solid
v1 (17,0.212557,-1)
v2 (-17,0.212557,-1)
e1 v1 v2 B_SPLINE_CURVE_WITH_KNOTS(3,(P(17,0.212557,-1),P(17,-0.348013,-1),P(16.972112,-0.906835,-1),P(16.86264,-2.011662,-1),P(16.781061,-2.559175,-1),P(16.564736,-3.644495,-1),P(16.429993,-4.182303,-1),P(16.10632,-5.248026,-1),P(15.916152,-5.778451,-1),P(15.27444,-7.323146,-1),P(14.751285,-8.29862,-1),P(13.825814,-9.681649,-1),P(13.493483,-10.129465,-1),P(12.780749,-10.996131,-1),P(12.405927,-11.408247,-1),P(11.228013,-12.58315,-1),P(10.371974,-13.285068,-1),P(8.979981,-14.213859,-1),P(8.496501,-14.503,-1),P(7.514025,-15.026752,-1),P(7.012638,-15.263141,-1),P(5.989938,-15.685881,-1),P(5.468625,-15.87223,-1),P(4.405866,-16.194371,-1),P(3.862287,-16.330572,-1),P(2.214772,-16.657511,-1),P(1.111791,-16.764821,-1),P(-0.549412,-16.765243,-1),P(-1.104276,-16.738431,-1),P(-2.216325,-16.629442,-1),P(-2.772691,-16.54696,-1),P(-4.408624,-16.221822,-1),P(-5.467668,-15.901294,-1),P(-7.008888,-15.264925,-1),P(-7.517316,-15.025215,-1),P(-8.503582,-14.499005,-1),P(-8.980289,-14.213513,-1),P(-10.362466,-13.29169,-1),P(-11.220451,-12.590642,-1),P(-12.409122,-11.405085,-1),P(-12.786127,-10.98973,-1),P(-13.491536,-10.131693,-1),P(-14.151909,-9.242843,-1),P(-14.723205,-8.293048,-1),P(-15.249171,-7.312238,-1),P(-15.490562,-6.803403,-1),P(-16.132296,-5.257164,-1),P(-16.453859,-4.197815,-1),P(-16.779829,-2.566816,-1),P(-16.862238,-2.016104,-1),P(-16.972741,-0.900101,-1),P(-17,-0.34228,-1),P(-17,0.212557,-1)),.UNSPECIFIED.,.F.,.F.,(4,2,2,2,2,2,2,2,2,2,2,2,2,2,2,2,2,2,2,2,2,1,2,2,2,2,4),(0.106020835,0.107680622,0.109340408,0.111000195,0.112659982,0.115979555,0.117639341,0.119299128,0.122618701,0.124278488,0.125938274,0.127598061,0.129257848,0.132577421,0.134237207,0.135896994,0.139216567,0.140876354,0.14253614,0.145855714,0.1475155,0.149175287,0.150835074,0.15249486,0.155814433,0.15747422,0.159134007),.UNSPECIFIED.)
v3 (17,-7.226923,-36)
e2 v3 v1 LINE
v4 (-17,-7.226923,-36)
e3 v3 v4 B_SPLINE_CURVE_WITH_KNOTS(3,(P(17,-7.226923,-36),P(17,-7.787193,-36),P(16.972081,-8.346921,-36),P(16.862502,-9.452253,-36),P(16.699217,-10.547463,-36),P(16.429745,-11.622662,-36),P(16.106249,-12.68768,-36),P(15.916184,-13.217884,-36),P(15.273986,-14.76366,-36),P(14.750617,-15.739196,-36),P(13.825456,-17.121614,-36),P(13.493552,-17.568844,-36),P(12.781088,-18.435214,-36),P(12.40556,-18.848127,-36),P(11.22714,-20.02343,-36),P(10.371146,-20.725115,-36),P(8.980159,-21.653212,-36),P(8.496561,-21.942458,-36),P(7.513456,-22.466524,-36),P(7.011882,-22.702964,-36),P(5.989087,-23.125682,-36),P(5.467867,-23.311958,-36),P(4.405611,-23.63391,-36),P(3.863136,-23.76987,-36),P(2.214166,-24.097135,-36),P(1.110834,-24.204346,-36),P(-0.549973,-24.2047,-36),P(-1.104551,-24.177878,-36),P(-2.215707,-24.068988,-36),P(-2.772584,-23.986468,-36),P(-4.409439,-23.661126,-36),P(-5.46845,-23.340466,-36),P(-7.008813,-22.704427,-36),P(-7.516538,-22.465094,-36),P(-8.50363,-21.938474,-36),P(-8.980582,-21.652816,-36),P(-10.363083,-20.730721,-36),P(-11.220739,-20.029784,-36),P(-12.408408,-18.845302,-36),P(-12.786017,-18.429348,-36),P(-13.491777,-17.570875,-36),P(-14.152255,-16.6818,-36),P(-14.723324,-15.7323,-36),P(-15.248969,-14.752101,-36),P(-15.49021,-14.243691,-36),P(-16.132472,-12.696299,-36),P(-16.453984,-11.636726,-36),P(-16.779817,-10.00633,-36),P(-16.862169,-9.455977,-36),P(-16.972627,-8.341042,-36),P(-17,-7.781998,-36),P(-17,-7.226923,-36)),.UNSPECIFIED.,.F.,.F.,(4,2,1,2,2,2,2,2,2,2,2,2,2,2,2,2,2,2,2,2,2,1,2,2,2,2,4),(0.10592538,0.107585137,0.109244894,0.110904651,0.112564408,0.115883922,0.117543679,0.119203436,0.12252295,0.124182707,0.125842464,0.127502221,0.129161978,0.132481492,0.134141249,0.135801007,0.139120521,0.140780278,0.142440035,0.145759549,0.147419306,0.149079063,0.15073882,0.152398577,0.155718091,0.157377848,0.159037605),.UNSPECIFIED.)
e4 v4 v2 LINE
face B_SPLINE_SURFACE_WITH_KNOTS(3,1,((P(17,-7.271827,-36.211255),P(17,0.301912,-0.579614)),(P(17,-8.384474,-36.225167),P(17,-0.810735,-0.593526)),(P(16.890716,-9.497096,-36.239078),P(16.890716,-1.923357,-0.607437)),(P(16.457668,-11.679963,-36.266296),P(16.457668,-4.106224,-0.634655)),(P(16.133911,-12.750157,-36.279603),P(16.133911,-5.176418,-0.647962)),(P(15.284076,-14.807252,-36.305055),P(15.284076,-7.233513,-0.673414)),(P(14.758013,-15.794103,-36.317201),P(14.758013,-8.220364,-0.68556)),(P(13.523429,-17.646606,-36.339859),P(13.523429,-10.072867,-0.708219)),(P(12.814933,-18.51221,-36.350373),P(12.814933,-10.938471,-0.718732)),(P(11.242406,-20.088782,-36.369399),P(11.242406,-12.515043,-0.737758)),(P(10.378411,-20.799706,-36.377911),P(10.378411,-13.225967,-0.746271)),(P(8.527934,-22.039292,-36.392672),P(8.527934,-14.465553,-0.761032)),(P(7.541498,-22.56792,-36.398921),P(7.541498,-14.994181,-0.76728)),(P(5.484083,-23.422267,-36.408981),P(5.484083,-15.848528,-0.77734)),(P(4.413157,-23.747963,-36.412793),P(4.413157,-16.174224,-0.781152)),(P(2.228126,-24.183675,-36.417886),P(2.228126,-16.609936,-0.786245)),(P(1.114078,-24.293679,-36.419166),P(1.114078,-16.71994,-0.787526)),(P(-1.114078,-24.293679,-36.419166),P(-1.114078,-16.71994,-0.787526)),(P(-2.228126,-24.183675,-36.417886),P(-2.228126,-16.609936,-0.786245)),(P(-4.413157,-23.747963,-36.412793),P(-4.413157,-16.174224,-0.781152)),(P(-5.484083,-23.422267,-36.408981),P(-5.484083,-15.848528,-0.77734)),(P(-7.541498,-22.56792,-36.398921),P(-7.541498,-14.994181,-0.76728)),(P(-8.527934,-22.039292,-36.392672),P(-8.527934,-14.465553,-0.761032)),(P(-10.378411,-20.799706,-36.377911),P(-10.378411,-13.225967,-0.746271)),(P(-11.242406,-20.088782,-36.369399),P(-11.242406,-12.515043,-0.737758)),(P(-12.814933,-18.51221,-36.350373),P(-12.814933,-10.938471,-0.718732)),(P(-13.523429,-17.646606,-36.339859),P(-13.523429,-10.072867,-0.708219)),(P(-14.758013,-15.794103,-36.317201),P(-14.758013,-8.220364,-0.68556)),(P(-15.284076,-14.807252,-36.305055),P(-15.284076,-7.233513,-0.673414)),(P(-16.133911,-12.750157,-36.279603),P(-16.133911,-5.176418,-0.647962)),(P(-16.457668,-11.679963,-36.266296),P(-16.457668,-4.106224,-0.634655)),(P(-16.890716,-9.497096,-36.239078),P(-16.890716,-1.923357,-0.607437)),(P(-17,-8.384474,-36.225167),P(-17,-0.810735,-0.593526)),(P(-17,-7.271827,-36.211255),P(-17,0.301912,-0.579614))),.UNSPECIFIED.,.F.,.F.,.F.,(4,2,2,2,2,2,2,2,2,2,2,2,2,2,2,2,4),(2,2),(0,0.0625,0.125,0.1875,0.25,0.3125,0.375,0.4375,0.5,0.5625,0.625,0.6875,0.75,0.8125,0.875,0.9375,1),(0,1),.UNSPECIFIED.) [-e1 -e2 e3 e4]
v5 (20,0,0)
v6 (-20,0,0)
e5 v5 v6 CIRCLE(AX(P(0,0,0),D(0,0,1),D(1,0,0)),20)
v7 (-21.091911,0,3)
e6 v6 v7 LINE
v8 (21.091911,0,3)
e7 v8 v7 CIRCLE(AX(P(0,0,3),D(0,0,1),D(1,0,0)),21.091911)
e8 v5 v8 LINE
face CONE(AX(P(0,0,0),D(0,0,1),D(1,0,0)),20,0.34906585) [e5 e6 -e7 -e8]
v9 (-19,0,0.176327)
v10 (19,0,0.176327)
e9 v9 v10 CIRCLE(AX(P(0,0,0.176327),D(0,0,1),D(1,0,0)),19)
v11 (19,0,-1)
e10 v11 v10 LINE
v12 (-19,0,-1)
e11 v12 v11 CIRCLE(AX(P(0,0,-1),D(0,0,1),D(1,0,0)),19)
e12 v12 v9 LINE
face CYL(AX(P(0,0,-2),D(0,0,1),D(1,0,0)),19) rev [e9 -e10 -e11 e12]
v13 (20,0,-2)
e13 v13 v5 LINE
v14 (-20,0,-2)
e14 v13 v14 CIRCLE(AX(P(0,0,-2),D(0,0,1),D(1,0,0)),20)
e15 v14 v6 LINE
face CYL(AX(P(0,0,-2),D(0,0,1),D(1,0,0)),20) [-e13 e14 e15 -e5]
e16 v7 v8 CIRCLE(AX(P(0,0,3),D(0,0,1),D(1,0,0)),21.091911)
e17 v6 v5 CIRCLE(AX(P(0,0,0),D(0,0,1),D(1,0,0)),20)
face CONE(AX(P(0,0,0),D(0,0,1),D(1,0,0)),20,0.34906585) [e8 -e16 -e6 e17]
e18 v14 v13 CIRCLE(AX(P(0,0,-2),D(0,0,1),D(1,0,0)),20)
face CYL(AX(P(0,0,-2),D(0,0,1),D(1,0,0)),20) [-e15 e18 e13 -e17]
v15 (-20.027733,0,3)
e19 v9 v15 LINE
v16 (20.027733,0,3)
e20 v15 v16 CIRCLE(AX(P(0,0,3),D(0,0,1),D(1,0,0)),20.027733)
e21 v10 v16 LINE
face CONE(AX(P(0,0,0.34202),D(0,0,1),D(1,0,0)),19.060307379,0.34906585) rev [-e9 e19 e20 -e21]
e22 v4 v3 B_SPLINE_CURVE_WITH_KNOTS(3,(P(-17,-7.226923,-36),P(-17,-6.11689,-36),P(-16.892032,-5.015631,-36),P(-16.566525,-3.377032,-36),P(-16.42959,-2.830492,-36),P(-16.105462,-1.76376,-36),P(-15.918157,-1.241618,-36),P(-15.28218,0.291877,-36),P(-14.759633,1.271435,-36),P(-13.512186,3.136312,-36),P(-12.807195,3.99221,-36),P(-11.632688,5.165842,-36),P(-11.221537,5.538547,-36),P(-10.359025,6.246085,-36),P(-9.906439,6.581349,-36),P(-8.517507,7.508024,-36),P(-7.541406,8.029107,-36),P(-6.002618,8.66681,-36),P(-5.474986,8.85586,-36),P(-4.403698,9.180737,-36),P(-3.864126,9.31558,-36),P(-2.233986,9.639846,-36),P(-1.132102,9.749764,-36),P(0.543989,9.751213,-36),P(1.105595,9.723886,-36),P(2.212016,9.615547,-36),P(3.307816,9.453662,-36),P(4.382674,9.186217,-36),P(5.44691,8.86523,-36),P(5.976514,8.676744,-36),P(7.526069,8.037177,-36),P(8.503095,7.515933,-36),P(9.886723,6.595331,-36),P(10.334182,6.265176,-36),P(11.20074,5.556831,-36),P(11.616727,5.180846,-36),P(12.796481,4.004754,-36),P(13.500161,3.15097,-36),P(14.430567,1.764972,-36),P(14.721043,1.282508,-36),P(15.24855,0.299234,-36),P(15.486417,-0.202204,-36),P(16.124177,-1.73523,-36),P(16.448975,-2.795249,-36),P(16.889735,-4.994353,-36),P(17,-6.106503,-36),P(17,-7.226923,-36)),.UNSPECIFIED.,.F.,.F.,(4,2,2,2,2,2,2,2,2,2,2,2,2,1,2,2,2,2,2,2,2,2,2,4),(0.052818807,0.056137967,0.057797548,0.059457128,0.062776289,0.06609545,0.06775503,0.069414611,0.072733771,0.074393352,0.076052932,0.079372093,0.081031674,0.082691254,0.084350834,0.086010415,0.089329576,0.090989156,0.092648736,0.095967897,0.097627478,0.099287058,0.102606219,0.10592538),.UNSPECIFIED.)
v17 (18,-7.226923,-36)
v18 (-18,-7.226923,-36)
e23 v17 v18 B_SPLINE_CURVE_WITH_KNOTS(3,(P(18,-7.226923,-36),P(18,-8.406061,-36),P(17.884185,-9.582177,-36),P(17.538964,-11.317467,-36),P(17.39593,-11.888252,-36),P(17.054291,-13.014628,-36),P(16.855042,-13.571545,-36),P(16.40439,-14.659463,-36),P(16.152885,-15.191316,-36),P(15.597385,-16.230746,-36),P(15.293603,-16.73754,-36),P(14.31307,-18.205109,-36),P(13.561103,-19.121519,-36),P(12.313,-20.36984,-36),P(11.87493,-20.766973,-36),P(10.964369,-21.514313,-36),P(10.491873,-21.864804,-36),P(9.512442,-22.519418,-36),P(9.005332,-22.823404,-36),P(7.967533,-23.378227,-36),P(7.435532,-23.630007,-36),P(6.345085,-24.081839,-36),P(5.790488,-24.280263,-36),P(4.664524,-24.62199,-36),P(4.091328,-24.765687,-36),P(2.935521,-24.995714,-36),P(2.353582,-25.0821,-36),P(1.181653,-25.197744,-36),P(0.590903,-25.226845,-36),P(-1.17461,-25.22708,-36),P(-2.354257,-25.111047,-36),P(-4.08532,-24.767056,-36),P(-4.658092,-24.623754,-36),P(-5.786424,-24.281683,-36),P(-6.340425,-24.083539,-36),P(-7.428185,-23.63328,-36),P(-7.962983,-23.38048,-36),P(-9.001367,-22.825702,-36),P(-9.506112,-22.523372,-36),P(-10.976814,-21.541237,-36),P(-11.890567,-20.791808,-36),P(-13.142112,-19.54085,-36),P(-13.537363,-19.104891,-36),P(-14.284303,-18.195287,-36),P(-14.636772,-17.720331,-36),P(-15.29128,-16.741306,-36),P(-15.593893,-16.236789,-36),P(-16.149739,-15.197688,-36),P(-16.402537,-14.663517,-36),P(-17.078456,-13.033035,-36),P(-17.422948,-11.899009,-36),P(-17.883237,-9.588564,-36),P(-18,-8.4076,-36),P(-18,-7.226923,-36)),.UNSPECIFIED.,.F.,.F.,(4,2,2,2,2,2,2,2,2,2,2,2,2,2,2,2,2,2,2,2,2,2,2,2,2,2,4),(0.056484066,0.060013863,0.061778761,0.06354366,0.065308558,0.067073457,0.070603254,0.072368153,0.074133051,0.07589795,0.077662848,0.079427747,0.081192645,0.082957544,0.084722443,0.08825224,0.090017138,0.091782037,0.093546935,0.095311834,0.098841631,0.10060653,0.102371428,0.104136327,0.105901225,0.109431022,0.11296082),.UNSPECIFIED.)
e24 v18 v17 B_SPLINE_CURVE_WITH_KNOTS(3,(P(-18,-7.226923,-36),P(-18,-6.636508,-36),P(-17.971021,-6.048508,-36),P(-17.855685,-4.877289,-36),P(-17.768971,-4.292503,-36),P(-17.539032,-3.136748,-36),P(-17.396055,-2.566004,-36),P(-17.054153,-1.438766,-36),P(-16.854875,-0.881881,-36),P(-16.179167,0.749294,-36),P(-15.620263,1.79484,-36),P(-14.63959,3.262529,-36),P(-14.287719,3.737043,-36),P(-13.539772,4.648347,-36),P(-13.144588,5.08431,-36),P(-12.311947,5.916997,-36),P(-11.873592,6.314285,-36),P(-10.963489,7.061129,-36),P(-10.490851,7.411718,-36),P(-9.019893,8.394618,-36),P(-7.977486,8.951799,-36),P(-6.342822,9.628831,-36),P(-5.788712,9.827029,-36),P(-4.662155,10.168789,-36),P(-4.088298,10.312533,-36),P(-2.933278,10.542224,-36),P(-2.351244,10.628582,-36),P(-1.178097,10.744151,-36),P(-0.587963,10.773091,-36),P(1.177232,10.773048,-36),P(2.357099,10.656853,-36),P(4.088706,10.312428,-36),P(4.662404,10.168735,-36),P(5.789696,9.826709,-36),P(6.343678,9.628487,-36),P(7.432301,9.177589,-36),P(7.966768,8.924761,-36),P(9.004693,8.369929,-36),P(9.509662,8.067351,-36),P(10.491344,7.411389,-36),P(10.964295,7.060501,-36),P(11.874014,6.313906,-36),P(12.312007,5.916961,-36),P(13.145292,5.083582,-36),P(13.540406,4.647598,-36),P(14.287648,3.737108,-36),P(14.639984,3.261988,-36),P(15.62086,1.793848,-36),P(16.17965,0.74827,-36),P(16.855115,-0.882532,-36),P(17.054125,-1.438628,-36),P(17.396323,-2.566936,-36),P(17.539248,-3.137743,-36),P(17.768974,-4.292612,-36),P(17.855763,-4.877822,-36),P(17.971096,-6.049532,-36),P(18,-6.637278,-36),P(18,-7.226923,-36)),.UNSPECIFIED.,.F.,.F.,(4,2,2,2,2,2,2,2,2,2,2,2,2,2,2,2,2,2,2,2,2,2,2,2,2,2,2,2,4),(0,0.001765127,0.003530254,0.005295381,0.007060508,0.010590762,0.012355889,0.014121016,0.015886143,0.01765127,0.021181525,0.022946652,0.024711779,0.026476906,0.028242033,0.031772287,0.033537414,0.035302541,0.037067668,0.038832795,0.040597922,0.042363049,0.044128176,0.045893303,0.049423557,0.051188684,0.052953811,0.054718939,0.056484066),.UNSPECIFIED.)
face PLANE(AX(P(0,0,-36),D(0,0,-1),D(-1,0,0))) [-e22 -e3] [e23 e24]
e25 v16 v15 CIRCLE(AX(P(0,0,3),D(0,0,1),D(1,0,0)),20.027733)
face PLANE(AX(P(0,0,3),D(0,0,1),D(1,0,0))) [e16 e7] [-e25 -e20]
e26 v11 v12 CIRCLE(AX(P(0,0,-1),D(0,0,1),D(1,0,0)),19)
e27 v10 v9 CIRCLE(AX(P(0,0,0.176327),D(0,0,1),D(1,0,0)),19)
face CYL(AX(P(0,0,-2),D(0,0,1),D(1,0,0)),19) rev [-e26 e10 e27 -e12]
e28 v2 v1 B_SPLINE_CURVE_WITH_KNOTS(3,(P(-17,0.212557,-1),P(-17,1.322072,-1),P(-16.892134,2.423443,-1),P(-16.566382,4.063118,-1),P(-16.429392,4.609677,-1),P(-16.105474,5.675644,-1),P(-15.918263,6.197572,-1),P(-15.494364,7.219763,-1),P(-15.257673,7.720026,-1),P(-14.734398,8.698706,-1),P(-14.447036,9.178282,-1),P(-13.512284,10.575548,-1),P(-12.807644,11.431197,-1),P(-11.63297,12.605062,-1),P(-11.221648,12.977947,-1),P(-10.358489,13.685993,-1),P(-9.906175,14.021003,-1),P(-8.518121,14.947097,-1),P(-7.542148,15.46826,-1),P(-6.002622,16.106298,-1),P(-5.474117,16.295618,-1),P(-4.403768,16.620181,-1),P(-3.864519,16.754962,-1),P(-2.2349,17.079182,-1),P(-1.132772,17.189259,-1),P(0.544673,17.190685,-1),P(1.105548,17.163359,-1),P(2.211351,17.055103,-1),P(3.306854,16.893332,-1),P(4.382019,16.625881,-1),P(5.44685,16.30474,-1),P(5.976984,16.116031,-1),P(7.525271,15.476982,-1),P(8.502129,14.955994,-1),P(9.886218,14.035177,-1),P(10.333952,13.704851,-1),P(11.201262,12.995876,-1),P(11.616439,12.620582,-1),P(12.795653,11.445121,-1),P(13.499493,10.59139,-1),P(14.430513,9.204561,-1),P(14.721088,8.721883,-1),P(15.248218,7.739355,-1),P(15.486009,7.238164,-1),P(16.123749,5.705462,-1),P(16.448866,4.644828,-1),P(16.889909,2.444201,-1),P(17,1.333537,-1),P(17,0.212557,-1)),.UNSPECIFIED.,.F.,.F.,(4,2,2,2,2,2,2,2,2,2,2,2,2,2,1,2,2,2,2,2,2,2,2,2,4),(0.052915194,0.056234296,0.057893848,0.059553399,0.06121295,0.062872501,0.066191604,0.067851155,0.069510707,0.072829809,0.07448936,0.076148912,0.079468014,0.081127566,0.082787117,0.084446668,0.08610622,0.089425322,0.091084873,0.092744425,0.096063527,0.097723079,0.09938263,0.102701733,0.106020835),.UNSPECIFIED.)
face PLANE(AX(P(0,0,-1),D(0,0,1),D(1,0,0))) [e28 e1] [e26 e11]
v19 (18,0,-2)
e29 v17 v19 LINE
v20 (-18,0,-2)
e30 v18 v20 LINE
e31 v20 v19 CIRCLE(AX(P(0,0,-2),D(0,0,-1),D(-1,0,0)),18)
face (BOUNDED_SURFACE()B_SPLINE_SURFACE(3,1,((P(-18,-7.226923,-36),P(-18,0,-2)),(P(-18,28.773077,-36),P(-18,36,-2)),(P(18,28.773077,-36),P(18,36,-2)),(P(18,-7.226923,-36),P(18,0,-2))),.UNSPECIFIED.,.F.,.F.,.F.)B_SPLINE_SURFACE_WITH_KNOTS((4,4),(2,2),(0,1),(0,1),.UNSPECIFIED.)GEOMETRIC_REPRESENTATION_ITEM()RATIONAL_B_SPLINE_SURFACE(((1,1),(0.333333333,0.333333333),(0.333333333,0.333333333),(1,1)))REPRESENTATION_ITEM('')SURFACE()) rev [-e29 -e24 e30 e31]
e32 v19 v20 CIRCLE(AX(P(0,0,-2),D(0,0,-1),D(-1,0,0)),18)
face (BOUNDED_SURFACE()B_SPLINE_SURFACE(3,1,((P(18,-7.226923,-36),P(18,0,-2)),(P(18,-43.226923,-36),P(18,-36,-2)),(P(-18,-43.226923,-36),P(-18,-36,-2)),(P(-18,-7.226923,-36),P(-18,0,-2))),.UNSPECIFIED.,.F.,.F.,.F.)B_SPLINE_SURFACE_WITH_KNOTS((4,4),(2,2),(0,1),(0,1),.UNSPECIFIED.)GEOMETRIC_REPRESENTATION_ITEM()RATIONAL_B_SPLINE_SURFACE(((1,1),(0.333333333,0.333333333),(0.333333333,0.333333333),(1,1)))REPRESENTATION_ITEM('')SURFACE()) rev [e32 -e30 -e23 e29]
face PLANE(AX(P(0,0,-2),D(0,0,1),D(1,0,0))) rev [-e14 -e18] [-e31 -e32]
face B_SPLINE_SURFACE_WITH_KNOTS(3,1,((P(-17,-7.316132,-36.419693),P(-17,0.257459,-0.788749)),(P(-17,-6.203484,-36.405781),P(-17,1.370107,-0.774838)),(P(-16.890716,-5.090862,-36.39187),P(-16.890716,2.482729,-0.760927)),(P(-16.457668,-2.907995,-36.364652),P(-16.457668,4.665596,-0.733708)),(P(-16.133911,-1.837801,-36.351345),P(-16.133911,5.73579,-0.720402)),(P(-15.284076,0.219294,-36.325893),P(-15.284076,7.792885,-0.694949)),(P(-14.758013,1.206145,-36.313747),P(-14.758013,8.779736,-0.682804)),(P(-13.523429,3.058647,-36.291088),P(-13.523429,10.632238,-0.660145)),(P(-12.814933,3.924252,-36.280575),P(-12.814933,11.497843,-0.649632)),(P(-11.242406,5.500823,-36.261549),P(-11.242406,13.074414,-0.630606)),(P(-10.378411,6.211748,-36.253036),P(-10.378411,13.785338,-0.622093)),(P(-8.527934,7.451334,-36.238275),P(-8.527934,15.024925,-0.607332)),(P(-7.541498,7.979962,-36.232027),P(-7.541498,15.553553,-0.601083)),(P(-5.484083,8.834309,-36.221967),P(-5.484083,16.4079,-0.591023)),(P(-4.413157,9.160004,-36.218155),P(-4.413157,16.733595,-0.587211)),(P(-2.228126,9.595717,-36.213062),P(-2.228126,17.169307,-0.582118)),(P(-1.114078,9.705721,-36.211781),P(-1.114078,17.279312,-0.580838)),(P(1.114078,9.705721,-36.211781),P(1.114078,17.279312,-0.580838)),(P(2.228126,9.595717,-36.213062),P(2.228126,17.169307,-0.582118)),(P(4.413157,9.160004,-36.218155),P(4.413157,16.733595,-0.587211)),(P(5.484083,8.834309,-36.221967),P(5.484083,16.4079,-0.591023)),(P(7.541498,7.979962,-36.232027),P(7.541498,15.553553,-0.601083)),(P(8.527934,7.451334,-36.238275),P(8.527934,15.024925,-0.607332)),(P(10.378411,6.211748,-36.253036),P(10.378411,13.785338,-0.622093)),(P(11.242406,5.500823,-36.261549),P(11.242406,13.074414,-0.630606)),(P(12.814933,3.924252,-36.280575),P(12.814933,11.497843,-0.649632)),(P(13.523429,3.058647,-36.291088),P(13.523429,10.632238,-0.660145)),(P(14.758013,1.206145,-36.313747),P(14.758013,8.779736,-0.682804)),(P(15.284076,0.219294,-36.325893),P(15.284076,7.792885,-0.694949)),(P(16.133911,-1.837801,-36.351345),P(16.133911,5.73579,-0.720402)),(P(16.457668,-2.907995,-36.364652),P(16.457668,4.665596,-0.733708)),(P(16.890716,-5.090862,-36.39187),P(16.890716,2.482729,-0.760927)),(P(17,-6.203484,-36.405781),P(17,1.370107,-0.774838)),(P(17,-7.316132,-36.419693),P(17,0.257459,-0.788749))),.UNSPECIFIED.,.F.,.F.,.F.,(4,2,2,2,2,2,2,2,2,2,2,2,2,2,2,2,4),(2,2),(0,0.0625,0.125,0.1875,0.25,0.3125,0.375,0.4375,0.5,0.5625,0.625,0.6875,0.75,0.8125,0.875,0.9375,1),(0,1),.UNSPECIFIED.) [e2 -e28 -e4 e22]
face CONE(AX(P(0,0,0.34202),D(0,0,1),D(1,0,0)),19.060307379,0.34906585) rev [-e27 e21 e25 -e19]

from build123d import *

# Parameters (mm, degrees)
SKETCH_1_R                = 20
EXTRUDE_1_DEPTH           = 3
EXTRUDE_1_TAPER           = -20
EXTRUDE_1_OTHER_WAY_DEPTH = 2
SKETCH_2_R                = 18
CUT_EXTRUDE_START         = 34
SKETCH_5_R                = 37.541334734
CUT_EXTRUDE_1_DEPTH       = 53
SHELL_1_T                 = -1


with BuildPart() as part:
    # 草图1 → 凸台-拉伸1 (new body)
    with BuildSketch(Plane.XY):
        Circle(SKETCH_1_R)
    extrude(amount=EXTRUDE_1_DEPTH, taper=EXTRUDE_1_TAPER)

    # 草图1 → 凸台-拉伸1 other way (add)
    with BuildSketch(Plane.XY):
        Circle(SKETCH_1_R)
    extrude(amount=-EXTRUDE_1_OTHER_WAY_DEPTH)

    # 扫描1: sweep along a path in 草图3
    with BuildLine(Plane(origin=(0, 0, 0), x_dir=(0, 0, -1), z_dir=(1, 0, 0))) as sweep_1_path:
        Line((2, 0), (46.016642033, -9.356026087))
    # 草图2 → 扫描1 (sweep)
    with BuildSketch(Plane(origin=(0, 0, -2), x_dir=(-1, 0, 0), z_dir=(0, 0, -1))):
        Circle(SKETCH_2_R)
    sweep(path=sweep_1_path.line)

    # 草图5 → 切除-拉伸1 (cut)
    with BuildSketch(Plane(origin=(0, 0, -2), x_dir=(-1, 0, 0), z_dir=(0, 0, -1)).offset(CUT_EXTRUDE_START)):
        Circle(SKETCH_5_R)
    extrude(amount=CUT_EXTRUDE_1_DEPTH, mode=Mode.SUBTRACT)

    # 抽壳1
    shell_1_openings = [part.faces().sort_by_distance(p)[0] for p in [
        (0, 0, 3),
        (-1.512e-06, -7.226932051, -36),
    ]]
    offset(amount=SHELL_1_T, openings=shell_1_openings, kind=Kind.INTERSECTION)


solid = part.part
